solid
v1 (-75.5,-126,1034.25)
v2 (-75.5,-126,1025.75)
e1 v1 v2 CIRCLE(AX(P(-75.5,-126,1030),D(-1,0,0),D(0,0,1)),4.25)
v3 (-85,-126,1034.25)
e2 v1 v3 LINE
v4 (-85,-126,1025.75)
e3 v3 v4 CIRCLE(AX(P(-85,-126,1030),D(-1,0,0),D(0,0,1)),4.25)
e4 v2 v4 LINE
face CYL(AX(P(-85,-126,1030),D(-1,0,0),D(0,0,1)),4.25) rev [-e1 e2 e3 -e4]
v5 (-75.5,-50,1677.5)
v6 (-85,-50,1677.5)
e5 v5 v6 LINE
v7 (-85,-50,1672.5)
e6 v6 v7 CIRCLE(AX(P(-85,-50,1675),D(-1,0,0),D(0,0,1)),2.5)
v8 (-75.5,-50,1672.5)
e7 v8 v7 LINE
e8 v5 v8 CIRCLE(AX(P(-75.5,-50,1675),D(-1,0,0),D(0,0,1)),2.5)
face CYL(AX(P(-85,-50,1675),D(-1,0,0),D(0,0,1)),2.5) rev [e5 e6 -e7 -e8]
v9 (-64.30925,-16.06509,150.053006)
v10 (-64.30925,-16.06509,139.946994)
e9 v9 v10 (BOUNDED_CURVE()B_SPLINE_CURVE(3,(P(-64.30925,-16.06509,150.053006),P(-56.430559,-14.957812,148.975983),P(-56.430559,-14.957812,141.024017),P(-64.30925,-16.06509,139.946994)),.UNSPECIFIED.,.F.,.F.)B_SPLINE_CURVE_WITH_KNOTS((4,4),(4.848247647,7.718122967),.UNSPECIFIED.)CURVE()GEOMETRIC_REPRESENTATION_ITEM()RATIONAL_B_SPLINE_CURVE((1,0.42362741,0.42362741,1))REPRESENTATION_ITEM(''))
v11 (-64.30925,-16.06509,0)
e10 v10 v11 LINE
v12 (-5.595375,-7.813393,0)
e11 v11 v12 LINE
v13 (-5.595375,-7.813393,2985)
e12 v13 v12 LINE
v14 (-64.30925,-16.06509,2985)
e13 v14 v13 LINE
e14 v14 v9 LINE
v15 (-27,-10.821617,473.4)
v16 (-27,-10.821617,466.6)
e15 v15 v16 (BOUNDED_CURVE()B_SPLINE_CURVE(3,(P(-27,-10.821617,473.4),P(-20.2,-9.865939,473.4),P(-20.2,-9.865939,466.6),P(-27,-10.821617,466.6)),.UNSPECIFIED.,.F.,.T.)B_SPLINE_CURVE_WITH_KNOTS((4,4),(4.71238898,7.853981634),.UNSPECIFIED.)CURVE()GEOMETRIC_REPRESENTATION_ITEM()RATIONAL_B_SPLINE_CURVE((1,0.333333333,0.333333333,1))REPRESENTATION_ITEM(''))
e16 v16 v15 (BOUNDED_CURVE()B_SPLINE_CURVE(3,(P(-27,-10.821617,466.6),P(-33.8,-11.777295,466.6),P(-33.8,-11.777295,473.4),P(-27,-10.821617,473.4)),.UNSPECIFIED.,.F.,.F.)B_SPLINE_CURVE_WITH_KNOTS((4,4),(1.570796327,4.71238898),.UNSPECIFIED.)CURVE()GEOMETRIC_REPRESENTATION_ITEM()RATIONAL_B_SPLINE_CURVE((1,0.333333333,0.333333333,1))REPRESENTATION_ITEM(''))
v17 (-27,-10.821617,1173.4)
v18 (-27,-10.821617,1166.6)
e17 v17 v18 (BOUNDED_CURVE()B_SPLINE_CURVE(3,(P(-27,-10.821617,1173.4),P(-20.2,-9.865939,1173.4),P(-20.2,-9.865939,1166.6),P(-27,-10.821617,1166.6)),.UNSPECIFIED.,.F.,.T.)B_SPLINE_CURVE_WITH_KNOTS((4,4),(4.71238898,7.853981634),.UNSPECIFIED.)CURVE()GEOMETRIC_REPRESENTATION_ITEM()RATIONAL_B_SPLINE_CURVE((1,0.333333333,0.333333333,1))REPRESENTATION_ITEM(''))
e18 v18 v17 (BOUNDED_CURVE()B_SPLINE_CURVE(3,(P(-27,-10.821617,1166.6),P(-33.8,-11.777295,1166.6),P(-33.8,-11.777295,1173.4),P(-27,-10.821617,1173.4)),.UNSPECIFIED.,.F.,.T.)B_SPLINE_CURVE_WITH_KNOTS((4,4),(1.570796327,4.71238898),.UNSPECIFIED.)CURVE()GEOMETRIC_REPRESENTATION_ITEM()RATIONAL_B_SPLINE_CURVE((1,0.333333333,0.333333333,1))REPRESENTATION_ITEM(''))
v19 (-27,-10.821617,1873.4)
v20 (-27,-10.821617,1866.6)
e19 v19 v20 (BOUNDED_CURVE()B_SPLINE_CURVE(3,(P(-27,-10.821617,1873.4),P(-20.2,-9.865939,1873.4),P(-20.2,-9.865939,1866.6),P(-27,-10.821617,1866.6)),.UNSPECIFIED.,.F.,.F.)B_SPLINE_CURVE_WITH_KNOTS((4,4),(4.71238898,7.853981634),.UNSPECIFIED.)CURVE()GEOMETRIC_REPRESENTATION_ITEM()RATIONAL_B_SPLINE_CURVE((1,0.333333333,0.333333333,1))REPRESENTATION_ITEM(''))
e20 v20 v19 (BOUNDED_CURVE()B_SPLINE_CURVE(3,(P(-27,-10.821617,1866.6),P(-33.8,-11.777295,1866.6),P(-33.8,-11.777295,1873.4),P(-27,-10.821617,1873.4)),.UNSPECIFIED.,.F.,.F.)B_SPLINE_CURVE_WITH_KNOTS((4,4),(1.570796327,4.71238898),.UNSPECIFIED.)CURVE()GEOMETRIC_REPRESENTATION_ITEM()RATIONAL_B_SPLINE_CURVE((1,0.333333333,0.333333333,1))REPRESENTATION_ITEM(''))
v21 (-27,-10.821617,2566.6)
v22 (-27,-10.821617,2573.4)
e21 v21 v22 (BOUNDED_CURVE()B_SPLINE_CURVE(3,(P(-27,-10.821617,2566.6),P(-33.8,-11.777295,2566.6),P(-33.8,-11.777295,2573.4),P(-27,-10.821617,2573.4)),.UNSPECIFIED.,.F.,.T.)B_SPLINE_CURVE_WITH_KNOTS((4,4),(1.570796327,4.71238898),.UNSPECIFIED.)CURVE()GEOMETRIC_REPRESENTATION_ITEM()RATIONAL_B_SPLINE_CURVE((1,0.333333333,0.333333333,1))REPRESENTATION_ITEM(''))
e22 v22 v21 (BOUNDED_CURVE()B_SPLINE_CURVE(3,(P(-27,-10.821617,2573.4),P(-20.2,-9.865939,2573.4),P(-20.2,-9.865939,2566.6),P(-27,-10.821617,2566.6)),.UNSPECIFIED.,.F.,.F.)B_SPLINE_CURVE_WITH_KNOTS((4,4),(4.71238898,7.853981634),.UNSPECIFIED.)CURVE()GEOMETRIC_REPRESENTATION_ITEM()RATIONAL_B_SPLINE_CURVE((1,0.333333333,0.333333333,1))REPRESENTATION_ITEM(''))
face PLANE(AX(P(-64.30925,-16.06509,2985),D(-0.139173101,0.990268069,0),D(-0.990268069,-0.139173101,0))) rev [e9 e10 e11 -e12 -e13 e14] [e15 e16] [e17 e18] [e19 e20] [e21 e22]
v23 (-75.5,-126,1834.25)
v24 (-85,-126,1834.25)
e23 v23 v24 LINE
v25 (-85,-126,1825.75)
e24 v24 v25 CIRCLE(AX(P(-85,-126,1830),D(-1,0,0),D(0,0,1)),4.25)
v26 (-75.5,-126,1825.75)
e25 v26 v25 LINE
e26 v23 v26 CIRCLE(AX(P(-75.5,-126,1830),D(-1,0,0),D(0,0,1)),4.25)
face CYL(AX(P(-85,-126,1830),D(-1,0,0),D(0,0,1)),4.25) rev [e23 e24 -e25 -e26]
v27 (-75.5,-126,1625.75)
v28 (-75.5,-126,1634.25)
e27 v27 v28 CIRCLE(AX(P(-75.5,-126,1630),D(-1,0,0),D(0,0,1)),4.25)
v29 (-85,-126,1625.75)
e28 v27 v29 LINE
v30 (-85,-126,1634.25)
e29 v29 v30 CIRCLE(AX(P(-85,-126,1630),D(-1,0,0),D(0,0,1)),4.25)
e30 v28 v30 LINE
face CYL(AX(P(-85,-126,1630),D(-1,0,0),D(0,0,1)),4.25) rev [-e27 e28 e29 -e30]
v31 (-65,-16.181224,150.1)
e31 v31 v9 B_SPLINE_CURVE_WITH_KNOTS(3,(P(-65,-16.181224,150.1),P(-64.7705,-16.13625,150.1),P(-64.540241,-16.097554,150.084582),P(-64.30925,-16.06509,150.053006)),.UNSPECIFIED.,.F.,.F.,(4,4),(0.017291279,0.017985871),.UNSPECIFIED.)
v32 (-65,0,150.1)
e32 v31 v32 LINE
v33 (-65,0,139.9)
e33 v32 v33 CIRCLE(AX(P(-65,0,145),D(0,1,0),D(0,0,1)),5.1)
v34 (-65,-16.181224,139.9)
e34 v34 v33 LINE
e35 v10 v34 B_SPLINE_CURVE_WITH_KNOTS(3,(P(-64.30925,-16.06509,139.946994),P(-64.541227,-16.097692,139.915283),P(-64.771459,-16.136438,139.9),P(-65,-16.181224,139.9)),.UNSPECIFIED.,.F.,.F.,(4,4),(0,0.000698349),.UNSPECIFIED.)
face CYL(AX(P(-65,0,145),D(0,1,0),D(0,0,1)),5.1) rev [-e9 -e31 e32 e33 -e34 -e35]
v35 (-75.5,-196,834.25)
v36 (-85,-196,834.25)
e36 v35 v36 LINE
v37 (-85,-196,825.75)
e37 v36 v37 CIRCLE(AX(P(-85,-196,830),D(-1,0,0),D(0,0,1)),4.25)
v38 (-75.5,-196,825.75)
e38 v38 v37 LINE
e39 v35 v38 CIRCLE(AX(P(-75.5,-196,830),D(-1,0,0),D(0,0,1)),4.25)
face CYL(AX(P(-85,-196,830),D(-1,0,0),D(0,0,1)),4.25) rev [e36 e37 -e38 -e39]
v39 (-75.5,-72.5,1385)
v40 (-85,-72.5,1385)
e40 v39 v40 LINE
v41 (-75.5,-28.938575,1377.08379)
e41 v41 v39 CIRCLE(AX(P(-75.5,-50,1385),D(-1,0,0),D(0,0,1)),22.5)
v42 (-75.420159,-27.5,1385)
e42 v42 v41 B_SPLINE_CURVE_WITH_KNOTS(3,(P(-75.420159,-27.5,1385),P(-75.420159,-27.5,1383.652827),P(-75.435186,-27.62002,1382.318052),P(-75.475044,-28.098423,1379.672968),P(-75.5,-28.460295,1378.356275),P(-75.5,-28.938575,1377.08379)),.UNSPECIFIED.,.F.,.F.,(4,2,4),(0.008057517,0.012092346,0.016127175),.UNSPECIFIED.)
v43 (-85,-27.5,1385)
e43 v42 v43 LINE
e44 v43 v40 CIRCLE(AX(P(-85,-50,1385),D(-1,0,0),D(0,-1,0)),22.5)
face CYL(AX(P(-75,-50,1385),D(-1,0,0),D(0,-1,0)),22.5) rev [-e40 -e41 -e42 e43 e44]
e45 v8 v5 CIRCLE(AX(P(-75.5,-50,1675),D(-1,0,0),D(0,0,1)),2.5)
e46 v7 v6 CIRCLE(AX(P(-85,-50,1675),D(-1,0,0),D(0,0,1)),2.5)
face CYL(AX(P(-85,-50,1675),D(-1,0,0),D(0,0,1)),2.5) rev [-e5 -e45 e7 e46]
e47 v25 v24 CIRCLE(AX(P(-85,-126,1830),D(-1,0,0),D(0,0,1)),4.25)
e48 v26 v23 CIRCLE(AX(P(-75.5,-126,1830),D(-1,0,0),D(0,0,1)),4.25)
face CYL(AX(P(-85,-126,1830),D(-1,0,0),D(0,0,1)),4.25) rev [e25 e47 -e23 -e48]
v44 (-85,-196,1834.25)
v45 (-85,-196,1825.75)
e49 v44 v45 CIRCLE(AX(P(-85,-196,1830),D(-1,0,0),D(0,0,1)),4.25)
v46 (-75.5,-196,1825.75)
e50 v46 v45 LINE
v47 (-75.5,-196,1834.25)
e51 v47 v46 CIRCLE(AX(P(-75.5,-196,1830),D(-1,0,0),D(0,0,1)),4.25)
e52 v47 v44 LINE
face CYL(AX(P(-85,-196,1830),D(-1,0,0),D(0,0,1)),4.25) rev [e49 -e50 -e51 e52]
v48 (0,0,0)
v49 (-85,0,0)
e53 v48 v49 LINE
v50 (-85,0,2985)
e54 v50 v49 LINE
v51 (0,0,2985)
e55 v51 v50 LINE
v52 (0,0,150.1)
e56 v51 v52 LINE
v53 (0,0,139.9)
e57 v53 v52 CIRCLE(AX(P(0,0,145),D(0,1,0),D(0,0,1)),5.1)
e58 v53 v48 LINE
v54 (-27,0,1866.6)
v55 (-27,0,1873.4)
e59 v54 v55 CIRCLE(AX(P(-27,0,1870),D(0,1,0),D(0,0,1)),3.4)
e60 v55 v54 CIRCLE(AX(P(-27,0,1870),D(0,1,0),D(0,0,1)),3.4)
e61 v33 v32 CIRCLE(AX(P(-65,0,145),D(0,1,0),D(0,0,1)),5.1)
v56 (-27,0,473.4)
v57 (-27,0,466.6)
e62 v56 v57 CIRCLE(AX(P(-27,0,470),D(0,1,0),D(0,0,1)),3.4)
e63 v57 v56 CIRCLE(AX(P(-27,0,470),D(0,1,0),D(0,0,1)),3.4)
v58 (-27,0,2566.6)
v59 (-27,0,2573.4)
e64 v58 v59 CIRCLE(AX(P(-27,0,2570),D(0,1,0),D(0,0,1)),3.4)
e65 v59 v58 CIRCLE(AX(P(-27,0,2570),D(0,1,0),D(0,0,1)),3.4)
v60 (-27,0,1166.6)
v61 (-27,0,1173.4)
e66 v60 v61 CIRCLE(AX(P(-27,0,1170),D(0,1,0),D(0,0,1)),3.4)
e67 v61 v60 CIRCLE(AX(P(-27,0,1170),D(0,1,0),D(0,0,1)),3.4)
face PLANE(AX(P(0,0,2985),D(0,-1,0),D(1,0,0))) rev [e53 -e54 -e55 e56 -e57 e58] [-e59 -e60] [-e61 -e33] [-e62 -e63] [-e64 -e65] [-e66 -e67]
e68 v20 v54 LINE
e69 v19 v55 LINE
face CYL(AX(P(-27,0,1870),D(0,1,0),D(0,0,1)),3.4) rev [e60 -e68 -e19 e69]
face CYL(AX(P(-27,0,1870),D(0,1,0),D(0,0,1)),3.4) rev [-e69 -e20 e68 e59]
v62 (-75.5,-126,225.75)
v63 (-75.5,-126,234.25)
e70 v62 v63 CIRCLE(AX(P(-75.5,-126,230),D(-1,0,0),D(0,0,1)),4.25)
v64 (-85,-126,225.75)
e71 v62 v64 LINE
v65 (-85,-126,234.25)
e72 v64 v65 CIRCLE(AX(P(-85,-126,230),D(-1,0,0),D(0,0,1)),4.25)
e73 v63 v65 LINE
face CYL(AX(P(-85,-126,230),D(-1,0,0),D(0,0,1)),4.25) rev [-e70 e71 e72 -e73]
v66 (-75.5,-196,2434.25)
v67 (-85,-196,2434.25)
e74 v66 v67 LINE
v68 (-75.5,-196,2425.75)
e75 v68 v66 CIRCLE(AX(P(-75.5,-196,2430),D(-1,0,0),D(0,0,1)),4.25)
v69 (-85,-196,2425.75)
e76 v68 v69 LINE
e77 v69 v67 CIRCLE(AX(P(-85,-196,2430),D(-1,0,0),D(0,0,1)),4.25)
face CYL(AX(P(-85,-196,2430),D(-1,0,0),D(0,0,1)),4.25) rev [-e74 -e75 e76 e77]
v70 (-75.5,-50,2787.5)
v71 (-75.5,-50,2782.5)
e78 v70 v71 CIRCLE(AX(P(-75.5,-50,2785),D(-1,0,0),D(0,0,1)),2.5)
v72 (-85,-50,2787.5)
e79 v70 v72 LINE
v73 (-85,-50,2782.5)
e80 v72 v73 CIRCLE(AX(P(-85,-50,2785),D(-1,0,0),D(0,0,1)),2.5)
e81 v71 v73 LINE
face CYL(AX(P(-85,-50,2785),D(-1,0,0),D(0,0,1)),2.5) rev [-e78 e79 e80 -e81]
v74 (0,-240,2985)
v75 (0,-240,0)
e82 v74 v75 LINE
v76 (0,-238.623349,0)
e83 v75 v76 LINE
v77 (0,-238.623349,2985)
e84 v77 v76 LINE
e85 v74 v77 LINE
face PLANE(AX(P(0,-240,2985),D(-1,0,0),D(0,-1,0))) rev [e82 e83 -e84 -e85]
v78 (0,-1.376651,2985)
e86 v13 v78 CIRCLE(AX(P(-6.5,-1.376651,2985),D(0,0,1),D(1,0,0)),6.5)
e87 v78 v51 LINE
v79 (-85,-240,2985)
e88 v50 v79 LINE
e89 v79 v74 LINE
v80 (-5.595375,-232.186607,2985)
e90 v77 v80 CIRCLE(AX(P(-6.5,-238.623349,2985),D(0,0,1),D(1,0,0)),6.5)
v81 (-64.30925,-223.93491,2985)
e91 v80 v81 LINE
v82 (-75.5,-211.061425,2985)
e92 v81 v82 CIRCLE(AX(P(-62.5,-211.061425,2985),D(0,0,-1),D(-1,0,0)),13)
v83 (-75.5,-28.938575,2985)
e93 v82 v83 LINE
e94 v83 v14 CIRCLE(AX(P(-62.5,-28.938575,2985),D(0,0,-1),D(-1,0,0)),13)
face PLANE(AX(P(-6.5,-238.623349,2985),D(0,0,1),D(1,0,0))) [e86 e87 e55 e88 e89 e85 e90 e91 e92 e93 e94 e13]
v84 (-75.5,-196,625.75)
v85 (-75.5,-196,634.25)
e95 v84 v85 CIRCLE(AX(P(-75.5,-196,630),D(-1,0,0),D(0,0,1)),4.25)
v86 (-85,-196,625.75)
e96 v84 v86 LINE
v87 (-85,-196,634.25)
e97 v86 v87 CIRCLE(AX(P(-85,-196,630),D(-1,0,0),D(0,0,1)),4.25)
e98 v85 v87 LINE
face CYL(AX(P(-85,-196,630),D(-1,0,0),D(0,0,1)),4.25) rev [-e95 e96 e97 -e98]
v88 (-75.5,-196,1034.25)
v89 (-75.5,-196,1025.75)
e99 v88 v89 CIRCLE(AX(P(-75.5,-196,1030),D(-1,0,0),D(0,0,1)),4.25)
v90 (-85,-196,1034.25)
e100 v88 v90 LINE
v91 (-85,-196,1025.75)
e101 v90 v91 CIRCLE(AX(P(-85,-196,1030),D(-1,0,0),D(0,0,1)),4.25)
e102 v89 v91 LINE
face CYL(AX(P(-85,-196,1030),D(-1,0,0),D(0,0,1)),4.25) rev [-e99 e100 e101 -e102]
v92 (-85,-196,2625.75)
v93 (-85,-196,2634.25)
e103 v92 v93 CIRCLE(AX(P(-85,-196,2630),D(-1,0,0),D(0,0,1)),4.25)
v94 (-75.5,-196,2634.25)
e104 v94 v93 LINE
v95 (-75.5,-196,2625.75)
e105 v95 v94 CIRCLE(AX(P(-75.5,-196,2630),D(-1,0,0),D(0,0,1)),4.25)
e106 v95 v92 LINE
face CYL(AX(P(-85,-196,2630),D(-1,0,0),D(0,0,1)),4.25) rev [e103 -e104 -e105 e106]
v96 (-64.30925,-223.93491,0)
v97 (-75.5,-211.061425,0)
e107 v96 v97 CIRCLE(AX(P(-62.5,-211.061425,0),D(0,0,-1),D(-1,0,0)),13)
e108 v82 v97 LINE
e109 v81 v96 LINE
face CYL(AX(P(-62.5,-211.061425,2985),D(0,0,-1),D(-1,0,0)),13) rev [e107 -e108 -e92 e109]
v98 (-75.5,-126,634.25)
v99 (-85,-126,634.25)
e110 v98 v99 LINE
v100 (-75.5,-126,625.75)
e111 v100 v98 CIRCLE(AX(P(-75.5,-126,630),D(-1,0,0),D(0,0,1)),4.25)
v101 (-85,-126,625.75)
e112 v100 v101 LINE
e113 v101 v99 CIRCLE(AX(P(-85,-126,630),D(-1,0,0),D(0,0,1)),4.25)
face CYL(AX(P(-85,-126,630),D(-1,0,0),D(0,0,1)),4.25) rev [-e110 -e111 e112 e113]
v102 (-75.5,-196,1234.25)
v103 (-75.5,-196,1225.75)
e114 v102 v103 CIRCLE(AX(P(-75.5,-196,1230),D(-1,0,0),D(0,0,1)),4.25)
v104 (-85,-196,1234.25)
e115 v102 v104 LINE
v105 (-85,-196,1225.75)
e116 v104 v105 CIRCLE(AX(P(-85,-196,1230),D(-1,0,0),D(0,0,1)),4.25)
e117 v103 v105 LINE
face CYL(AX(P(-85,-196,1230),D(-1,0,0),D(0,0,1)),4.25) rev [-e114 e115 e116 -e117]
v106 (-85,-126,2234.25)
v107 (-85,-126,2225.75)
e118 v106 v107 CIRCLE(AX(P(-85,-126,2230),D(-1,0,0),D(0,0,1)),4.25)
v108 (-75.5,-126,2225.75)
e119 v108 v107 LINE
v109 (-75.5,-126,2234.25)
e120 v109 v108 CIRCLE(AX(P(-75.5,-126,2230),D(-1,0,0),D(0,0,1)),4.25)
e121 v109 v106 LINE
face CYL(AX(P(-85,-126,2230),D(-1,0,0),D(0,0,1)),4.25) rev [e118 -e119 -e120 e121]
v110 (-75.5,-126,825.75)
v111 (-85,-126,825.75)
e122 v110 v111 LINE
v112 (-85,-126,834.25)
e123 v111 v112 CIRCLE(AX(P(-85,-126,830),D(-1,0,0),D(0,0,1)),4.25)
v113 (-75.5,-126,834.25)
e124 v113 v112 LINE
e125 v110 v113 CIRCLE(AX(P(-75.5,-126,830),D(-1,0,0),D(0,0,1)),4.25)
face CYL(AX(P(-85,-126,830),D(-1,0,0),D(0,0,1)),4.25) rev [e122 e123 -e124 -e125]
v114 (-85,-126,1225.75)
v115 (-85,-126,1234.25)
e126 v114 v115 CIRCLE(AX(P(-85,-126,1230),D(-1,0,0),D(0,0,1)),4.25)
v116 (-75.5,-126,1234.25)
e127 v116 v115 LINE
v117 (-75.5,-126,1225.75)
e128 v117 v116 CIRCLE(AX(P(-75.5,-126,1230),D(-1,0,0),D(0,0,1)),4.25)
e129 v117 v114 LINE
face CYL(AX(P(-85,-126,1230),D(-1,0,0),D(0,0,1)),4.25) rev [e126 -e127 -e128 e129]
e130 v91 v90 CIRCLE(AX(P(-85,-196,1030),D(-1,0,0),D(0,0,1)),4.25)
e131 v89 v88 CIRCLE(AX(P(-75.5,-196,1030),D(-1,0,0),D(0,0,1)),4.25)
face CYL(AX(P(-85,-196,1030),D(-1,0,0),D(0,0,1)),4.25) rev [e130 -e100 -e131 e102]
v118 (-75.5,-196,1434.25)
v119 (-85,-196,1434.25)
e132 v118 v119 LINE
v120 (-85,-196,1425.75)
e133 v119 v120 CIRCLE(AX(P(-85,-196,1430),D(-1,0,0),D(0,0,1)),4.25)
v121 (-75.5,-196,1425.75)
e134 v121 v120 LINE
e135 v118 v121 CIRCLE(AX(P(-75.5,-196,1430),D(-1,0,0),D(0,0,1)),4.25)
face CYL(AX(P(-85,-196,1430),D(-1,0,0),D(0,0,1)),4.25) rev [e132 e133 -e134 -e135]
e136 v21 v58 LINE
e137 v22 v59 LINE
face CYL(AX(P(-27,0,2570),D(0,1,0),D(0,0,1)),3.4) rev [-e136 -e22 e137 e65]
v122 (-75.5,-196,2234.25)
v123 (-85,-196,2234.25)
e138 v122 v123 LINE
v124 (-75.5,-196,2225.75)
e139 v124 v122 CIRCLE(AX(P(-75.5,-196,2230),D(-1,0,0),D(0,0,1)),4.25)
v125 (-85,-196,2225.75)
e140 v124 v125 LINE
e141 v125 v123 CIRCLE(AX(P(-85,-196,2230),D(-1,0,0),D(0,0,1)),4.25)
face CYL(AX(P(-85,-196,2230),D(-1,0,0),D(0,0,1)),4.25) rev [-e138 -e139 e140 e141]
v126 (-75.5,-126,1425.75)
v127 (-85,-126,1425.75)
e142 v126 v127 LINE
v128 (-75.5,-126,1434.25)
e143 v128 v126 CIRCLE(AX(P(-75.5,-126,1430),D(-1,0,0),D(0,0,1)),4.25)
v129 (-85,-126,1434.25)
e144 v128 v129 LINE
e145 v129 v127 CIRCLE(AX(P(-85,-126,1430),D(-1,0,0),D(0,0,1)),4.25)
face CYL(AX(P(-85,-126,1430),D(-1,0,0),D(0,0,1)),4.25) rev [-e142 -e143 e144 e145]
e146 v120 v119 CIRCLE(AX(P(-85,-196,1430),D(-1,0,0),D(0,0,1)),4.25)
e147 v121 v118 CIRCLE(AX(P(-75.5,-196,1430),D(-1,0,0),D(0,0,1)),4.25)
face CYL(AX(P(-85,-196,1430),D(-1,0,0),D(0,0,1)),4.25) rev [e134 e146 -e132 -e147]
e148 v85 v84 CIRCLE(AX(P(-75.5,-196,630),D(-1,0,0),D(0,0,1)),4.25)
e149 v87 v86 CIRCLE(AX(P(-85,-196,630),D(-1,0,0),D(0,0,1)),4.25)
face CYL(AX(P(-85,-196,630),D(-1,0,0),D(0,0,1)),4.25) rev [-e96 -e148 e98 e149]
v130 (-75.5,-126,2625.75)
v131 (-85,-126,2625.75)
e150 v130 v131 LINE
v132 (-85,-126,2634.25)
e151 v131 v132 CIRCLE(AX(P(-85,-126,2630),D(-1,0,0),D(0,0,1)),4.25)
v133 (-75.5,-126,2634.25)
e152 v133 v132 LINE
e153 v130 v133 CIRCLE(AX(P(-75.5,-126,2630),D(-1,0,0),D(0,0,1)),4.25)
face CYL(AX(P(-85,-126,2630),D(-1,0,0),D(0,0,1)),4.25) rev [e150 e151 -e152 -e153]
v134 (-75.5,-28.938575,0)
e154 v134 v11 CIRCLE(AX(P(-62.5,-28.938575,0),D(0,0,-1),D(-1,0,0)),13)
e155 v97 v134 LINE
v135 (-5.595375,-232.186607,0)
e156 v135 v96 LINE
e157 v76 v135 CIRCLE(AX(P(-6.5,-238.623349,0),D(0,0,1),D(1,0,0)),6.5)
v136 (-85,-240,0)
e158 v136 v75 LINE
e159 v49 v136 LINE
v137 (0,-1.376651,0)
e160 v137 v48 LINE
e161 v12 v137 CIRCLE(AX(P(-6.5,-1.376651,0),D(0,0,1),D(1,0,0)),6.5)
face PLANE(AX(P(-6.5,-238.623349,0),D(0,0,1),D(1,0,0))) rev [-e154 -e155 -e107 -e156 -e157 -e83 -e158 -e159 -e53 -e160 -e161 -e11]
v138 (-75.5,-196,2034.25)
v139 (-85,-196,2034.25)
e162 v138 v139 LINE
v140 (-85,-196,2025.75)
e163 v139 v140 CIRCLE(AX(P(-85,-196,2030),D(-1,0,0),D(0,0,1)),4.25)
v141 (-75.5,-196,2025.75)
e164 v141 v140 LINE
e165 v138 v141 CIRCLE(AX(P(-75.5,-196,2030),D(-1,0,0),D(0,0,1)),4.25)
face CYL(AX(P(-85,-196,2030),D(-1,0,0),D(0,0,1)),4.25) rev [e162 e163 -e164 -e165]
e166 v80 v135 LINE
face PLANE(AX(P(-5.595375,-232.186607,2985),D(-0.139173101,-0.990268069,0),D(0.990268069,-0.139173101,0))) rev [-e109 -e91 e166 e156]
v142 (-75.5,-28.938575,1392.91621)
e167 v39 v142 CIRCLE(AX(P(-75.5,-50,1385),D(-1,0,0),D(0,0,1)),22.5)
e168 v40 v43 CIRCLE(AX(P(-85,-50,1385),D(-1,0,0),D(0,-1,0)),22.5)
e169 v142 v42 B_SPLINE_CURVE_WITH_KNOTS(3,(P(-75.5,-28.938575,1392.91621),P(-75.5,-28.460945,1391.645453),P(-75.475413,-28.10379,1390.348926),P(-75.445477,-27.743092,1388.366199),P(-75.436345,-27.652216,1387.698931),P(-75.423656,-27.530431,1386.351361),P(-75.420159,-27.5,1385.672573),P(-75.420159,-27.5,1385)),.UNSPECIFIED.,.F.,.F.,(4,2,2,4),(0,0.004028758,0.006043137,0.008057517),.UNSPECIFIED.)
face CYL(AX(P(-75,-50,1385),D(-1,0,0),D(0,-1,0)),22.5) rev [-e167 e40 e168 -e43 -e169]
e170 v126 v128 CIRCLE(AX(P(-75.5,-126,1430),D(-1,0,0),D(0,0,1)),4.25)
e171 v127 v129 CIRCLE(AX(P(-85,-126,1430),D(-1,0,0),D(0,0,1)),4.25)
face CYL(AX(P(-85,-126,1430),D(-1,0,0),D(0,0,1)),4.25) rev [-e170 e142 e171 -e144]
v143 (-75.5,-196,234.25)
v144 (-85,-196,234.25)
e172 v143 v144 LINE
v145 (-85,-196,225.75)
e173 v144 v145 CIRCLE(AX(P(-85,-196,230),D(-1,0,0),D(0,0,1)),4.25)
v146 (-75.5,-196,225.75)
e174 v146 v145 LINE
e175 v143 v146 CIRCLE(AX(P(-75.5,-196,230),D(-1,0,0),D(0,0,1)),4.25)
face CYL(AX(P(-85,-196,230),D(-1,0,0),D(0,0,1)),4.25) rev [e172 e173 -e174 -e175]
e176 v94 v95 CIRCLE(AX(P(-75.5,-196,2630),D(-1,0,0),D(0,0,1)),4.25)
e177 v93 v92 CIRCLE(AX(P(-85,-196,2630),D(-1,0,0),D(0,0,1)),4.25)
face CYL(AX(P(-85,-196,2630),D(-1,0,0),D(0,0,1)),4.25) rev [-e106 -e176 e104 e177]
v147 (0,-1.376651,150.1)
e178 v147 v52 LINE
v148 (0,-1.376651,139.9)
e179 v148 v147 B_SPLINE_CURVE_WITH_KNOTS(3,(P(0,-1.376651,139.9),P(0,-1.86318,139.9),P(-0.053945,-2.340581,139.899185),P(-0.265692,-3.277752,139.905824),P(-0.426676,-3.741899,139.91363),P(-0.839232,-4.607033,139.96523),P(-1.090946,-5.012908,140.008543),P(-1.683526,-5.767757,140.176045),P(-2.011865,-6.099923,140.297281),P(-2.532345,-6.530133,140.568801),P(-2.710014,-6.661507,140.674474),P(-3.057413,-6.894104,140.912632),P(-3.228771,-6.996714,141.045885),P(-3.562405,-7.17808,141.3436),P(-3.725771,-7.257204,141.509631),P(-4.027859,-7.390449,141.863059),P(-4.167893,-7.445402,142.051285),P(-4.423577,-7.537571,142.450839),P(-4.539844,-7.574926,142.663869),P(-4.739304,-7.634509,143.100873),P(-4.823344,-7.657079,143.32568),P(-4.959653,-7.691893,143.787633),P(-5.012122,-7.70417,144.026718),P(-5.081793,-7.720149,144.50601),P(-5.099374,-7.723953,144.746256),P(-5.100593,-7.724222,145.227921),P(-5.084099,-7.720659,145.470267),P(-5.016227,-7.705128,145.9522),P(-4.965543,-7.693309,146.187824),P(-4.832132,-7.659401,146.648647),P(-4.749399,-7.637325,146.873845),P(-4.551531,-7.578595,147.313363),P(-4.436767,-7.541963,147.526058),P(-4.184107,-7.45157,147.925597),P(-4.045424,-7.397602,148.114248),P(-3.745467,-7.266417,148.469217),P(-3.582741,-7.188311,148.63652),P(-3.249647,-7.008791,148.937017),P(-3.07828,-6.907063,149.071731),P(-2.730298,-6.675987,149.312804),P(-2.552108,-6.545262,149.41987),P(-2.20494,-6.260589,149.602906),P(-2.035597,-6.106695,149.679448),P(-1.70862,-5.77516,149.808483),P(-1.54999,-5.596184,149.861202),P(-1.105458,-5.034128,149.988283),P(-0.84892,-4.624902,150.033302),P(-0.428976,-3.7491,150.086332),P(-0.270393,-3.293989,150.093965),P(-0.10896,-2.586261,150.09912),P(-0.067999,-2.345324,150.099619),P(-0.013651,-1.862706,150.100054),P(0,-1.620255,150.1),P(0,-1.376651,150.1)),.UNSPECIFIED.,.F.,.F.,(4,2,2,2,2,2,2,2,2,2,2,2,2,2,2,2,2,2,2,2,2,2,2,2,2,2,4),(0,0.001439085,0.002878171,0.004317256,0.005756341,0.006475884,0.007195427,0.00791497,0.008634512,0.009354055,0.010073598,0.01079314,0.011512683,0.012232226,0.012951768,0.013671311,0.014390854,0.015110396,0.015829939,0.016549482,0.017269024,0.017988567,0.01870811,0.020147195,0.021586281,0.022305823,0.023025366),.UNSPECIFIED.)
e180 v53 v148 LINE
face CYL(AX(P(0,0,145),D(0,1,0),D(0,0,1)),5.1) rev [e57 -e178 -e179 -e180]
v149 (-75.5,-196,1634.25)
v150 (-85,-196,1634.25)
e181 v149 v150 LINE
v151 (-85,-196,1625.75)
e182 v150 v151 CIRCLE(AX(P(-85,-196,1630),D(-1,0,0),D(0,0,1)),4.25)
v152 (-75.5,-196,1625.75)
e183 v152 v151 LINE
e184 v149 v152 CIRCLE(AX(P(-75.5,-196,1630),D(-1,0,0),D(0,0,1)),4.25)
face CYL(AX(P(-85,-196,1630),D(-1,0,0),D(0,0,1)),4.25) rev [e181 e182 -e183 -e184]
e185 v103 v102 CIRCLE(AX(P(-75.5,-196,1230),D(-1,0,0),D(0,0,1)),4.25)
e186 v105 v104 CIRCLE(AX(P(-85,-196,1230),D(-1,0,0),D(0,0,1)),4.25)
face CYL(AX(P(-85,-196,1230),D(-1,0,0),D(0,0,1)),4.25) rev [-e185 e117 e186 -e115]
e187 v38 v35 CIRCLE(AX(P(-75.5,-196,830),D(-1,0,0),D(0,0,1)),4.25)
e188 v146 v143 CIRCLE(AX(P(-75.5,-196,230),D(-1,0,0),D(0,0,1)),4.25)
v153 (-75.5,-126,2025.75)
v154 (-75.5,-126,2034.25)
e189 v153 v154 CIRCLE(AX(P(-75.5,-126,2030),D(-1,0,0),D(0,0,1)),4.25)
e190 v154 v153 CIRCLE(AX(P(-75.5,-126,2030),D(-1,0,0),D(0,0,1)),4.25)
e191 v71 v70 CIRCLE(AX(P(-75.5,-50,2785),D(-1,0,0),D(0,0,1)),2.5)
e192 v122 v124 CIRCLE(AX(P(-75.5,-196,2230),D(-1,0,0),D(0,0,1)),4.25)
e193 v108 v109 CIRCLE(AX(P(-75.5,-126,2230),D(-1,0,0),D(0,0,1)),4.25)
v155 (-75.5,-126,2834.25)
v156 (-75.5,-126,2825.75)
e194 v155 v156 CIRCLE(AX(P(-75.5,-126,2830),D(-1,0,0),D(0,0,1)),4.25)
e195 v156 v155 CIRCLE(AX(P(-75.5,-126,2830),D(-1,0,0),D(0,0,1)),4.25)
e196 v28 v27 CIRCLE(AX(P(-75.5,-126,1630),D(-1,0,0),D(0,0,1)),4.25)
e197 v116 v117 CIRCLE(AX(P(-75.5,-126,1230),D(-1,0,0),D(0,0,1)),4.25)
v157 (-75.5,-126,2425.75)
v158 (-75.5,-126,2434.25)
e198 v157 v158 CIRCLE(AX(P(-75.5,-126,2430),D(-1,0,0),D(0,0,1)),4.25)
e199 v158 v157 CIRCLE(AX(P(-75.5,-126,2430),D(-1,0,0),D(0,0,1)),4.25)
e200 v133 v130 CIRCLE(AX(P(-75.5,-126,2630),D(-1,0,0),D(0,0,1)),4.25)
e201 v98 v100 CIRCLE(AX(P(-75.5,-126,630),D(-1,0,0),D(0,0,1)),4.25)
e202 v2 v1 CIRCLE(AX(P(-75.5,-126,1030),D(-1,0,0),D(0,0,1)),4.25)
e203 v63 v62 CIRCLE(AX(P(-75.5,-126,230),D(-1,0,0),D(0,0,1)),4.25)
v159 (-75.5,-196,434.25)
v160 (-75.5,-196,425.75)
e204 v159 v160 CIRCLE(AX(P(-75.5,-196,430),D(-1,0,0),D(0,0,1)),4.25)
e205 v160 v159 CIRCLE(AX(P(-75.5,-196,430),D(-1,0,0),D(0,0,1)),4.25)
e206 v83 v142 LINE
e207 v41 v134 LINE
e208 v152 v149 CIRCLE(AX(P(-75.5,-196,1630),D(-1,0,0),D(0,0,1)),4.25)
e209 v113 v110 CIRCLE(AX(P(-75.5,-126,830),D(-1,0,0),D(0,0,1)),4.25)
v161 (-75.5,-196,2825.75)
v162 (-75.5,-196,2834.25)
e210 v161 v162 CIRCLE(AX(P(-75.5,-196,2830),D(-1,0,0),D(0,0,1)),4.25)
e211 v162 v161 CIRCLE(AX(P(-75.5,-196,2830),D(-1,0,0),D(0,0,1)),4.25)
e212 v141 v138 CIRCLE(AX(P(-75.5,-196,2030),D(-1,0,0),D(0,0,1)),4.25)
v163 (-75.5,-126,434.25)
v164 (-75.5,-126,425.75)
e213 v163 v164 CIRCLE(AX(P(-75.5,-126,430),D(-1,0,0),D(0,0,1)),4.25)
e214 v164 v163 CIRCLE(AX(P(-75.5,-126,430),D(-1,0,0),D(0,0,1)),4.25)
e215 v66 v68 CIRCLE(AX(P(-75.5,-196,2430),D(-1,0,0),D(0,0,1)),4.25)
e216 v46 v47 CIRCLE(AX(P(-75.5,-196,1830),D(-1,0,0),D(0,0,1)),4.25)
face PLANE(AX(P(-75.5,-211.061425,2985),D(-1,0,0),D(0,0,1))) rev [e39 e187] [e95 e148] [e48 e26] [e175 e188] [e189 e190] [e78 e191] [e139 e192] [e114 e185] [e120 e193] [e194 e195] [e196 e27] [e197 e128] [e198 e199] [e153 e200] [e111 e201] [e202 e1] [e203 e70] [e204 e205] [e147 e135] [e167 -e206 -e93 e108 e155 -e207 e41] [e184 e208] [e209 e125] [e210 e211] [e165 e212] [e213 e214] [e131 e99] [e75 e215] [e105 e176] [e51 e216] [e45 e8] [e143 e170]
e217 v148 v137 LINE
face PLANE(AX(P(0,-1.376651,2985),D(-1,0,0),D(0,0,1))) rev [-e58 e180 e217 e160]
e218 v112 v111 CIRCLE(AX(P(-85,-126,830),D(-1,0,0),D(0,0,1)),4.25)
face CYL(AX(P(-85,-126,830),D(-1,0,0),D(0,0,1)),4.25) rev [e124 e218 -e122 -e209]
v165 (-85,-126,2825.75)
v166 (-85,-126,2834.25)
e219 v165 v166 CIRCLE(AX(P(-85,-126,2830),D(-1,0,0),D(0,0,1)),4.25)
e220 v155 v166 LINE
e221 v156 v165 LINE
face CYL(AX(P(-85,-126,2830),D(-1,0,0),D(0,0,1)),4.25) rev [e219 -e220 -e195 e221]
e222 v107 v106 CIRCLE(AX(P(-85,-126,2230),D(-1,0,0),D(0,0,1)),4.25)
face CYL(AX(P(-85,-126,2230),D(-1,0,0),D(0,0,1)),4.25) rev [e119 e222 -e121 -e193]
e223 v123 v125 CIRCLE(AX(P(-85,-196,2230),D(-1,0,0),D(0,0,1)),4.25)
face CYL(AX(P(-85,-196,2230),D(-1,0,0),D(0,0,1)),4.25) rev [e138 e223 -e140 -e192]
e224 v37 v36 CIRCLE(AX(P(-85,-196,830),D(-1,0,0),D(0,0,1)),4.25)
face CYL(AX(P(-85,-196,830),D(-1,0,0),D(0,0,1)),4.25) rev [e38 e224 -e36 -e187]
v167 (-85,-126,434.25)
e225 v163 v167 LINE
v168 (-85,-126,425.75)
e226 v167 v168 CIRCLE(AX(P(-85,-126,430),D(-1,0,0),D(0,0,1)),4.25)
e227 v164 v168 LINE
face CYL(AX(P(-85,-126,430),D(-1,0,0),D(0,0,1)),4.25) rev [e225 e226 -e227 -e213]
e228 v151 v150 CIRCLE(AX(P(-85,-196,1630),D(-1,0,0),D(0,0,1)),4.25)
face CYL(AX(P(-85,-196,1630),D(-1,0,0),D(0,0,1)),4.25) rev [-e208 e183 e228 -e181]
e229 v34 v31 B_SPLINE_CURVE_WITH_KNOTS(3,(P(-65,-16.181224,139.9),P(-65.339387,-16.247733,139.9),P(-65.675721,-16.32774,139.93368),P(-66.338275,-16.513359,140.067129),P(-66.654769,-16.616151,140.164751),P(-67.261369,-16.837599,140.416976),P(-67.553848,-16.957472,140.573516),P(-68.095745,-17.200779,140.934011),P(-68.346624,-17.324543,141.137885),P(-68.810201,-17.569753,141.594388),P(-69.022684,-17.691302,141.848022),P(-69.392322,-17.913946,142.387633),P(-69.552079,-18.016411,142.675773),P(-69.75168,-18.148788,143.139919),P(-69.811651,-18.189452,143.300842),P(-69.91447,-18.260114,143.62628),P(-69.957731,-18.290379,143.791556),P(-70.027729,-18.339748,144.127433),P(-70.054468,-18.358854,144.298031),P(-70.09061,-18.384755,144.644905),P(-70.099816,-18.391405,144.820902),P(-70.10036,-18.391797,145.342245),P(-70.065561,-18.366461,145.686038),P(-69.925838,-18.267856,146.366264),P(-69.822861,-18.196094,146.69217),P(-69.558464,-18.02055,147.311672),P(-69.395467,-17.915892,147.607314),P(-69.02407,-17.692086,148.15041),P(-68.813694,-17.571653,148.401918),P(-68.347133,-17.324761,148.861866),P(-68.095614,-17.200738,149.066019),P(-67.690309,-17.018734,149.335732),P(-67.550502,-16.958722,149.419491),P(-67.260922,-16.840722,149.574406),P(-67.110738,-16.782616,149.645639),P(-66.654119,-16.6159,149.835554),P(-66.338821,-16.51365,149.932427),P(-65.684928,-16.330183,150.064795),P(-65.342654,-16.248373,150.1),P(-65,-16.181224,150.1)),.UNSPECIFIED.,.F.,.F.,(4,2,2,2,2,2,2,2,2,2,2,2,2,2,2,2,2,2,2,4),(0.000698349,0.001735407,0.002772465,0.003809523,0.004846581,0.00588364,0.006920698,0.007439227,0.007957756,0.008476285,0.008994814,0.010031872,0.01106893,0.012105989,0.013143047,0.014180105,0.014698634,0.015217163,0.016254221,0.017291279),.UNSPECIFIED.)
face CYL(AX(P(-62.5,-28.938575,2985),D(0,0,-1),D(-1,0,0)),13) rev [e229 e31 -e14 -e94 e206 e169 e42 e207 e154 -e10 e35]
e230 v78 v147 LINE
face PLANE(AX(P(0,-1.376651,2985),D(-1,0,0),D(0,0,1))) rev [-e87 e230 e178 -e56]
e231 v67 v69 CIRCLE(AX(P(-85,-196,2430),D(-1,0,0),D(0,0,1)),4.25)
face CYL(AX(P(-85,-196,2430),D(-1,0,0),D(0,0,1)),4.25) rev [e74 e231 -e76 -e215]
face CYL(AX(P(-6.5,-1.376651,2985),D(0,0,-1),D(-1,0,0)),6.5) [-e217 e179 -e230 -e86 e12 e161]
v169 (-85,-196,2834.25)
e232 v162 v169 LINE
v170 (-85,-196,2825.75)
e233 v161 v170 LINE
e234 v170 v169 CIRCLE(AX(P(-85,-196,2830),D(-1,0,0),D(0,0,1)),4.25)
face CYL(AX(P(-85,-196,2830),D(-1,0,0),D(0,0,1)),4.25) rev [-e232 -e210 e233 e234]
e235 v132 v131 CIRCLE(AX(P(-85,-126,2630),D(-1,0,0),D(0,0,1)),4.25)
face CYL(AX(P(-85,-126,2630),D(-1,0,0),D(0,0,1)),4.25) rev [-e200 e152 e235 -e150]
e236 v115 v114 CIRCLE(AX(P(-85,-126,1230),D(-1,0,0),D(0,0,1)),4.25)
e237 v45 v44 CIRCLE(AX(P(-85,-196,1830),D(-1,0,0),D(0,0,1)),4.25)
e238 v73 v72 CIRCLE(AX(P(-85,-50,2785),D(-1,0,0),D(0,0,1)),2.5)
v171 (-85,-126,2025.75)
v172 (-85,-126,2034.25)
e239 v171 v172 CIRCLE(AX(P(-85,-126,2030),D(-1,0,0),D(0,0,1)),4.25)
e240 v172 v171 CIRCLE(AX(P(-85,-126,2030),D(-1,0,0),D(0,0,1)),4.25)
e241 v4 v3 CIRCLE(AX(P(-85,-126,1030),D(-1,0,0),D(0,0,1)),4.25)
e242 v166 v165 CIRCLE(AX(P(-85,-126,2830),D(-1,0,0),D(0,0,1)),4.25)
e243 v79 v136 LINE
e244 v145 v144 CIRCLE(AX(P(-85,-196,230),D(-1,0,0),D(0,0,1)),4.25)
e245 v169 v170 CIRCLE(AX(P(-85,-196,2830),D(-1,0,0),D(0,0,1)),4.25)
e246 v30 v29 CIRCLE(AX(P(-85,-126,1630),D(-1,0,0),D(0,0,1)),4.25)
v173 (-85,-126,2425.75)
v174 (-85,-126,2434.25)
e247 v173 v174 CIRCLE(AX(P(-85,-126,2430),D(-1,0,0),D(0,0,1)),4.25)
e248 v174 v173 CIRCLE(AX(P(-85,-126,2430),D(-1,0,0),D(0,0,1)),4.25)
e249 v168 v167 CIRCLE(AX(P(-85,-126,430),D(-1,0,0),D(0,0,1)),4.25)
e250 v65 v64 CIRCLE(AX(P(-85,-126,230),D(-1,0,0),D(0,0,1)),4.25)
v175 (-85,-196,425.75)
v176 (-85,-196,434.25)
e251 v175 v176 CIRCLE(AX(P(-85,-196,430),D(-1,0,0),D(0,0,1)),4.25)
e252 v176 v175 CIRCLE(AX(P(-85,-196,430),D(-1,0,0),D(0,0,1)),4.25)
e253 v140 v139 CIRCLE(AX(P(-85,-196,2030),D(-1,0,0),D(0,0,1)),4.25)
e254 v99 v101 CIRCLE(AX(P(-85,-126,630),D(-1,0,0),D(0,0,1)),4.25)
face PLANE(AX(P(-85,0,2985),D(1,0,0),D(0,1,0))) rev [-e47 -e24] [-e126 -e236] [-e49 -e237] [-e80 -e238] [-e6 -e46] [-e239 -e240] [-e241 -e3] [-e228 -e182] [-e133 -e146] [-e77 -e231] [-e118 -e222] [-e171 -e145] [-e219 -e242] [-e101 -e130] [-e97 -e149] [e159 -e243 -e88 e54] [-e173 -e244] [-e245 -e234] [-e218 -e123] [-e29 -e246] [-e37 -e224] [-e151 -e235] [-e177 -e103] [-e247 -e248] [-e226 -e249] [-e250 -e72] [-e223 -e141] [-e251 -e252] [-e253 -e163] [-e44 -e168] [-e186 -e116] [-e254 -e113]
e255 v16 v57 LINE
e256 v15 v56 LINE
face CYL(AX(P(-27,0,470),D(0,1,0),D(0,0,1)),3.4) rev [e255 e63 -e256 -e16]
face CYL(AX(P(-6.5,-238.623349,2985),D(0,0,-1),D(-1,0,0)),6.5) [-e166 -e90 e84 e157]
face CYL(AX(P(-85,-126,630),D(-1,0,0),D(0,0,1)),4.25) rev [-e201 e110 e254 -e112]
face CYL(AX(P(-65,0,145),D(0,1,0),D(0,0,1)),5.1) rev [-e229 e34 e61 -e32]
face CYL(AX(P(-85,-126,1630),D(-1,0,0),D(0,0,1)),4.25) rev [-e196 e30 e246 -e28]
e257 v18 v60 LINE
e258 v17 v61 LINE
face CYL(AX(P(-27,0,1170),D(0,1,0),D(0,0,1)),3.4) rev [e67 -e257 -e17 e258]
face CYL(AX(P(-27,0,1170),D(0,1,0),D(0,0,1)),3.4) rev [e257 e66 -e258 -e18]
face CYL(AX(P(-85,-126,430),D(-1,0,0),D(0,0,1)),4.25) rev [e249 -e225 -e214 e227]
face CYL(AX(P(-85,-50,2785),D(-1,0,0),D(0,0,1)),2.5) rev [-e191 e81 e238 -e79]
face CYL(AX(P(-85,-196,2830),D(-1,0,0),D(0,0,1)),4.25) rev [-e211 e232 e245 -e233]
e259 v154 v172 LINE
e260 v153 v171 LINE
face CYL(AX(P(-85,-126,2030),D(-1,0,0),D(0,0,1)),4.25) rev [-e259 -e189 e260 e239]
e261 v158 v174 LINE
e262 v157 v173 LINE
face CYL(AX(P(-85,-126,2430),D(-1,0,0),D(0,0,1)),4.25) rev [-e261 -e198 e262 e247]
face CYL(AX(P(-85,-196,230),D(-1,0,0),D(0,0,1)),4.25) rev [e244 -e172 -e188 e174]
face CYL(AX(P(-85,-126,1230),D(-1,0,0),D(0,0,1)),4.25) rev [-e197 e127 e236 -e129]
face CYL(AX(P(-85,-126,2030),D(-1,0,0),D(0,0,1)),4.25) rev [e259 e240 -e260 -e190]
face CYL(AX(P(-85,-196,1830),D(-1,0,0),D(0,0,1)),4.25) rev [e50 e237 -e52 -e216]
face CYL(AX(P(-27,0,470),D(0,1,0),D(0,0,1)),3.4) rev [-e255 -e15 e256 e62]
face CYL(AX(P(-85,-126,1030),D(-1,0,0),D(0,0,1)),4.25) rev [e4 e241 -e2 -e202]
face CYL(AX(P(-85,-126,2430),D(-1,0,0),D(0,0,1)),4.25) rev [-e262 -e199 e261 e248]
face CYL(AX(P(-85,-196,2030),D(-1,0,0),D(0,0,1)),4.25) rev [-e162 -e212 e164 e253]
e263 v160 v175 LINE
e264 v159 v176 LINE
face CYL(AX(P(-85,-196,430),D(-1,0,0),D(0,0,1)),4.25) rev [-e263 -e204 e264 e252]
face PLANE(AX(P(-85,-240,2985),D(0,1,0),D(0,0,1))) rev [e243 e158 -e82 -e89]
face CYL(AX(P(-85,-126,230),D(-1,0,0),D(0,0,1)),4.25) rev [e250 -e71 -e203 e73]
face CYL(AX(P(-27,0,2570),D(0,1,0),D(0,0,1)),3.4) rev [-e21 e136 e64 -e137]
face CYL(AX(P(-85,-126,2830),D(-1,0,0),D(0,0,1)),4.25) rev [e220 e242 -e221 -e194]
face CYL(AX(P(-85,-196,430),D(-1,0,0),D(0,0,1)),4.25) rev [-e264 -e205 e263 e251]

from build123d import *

# Parameters (mm, degrees)
EXTRUDE_1_DEPTH         = 2985
HOLE_WIZARD_M10_2_D     = 8.5
HOLE_WIZARD_M10_2_DEPTH = 24.5
HOLE_WIZARD_M10_2_TIP   = 2.553657631
HOLE_WIZARD_M8_1_D      = 6.8
HOLE_WIZARD_M8_1_DEPTH  = 19.75
HOLE_WIZARD_M8_1_TIP    = 2.042926105
HOLE_WIZARD_M12_1_D     = 10.2
HOLE_WIZARD_M12_1_DEPTH = 29.25
HOLE_WIZARD_M12_1_TIP   = 3.064389157
SKETCH_13_R             = 22.5
CUT_EXTRUDE_1_DEPTH     = 10
HOLE_WIZARD_M6_1_D      = 5
HOLE_WIZARD_M6_1_DEPTH  = 15
HOLE_WIZARD_M6_1_TIP    = 1.502151548


with BuildPart() as part:
    # 草图1 → 凸台-拉伸1 (new body)
    with BuildSketch(Plane.XY):
        with BuildLine():
            Line((0, 0), (-85, 0))
            Line((-85, 0), (-85, -240))
            Line((-85, -240), (0, -240))
            Line((0, -240), (0, -238.623349271))
            ThreePointArc((0, -238.623349271), (-1.594387729, -234.358965582), (-5.595374844, -232.186606824))
            Line((-5.595374844, -232.186606824), (-64.309250312, -223.934909757))
            ThreePointArc((-64.309250312, -223.934909757), (-72.311224543, -219.59019224), (-75.5, -211.061424863))
            Line((-75.5, -211.061424863), (-75.5, -28.938575137))
            ThreePointArc((-75.5, -28.938575137), (-72.311224543, -20.40980776), (-64.309250312, -16.065090243))
            Line((-64.309250312, -16.065090243), (-5.595374844, -7.813393176))
            ThreePointArc((-5.595374844, -7.813393176), (-1.594387729, -5.641034418), (0, -1.376650729))
            Line((0, -1.376650729), (0, 0))
        make_face()
    extrude(amount=EXTRUDE_1_DEPTH)

    # M10 螺纹孔2
    with Locations(Plane.ZY.offset(85)):
        with Locations((230, -126), (230, -196), (430, -126), (430, -196), (630, -126), (630, -196), (830, -126), (830, -196), (1030, -126), (1030, -196), (1230, -126), (1230, -196), (1430, -126), (1430, -196), (1630, -196), (1630, -126), (1830, -196), (1830, -126), (2030, -126), (2030, -196), (2230, -196), (2230, -126), (2430, -126), (2430, -196), (2630, -196), (2630, -126), (2830, -126), (2830, -196)):
            Hole(HOLE_WIZARD_M10_2_D / 2, depth=HOLE_WIZARD_M10_2_DEPTH)
            with Locations((0, 0, -(HOLE_WIZARD_M10_2_DEPTH + HOLE_WIZARD_M10_2_TIP / 2))):  # 118° drill point
                Cone(0, HOLE_WIZARD_M10_2_D / 2, HOLE_WIZARD_M10_2_TIP, mode=Mode.SUBTRACT)

    # M8 螺纹孔1
    with Locations(Plane(origin=(0, 0, 0), x_dir=(1, 0, 0), z_dir=(0, 1, 0))):
        with Locations((-27, -470), (-27, -1170), (-27, -1870), (-27, -2570)):
            Hole(HOLE_WIZARD_M8_1_D / 2, depth=HOLE_WIZARD_M8_1_DEPTH)
            with Locations((0, 0, -(HOLE_WIZARD_M8_1_DEPTH + HOLE_WIZARD_M8_1_TIP / 2))):  # 118° drill point
                Cone(0, HOLE_WIZARD_M8_1_D / 2, HOLE_WIZARD_M8_1_TIP, mode=Mode.SUBTRACT)

    # M12 螺纹孔1
    with Locations(Plane(origin=(0, 0, 0), x_dir=(1, 0, 0), z_dir=(0, 1, 0))):
        with Locations((-65, -145), (0, -145)):
            Hole(HOLE_WIZARD_M12_1_D / 2, depth=HOLE_WIZARD_M12_1_DEPTH)
            with Locations((0, 0, -(HOLE_WIZARD_M12_1_DEPTH + HOLE_WIZARD_M12_1_TIP / 2))):  # 118° drill point
                Cone(0, HOLE_WIZARD_M12_1_D / 2, HOLE_WIZARD_M12_1_TIP, mode=Mode.SUBTRACT)

    # 草图13 → 切除-拉伸1 (cut)
    with BuildSketch(Plane.ZY.offset(85)):
        with Locations(Location((1385, -50, 0), (0, 0, 270))):
            Circle(SKETCH_13_R)
    extrude(amount=-CUT_EXTRUDE_1_DEPTH, mode=Mode.SUBTRACT)

    # M6 螺纹孔1
    with Locations(Plane.ZY.offset(85)):
        with Locations((1675, -50), (2785, -50)):
            Hole(HOLE_WIZARD_M6_1_D / 2, depth=HOLE_WIZARD_M6_1_DEPTH)
            with Locations((0, 0, -(HOLE_WIZARD_M6_1_DEPTH + HOLE_WIZARD_M6_1_TIP / 2))):  # 118° drill point
                Cone(0, HOLE_WIZARD_M6_1_D / 2, HOLE_WIZARD_M6_1_TIP, mode=Mode.SUBTRACT)


solid = part.part
